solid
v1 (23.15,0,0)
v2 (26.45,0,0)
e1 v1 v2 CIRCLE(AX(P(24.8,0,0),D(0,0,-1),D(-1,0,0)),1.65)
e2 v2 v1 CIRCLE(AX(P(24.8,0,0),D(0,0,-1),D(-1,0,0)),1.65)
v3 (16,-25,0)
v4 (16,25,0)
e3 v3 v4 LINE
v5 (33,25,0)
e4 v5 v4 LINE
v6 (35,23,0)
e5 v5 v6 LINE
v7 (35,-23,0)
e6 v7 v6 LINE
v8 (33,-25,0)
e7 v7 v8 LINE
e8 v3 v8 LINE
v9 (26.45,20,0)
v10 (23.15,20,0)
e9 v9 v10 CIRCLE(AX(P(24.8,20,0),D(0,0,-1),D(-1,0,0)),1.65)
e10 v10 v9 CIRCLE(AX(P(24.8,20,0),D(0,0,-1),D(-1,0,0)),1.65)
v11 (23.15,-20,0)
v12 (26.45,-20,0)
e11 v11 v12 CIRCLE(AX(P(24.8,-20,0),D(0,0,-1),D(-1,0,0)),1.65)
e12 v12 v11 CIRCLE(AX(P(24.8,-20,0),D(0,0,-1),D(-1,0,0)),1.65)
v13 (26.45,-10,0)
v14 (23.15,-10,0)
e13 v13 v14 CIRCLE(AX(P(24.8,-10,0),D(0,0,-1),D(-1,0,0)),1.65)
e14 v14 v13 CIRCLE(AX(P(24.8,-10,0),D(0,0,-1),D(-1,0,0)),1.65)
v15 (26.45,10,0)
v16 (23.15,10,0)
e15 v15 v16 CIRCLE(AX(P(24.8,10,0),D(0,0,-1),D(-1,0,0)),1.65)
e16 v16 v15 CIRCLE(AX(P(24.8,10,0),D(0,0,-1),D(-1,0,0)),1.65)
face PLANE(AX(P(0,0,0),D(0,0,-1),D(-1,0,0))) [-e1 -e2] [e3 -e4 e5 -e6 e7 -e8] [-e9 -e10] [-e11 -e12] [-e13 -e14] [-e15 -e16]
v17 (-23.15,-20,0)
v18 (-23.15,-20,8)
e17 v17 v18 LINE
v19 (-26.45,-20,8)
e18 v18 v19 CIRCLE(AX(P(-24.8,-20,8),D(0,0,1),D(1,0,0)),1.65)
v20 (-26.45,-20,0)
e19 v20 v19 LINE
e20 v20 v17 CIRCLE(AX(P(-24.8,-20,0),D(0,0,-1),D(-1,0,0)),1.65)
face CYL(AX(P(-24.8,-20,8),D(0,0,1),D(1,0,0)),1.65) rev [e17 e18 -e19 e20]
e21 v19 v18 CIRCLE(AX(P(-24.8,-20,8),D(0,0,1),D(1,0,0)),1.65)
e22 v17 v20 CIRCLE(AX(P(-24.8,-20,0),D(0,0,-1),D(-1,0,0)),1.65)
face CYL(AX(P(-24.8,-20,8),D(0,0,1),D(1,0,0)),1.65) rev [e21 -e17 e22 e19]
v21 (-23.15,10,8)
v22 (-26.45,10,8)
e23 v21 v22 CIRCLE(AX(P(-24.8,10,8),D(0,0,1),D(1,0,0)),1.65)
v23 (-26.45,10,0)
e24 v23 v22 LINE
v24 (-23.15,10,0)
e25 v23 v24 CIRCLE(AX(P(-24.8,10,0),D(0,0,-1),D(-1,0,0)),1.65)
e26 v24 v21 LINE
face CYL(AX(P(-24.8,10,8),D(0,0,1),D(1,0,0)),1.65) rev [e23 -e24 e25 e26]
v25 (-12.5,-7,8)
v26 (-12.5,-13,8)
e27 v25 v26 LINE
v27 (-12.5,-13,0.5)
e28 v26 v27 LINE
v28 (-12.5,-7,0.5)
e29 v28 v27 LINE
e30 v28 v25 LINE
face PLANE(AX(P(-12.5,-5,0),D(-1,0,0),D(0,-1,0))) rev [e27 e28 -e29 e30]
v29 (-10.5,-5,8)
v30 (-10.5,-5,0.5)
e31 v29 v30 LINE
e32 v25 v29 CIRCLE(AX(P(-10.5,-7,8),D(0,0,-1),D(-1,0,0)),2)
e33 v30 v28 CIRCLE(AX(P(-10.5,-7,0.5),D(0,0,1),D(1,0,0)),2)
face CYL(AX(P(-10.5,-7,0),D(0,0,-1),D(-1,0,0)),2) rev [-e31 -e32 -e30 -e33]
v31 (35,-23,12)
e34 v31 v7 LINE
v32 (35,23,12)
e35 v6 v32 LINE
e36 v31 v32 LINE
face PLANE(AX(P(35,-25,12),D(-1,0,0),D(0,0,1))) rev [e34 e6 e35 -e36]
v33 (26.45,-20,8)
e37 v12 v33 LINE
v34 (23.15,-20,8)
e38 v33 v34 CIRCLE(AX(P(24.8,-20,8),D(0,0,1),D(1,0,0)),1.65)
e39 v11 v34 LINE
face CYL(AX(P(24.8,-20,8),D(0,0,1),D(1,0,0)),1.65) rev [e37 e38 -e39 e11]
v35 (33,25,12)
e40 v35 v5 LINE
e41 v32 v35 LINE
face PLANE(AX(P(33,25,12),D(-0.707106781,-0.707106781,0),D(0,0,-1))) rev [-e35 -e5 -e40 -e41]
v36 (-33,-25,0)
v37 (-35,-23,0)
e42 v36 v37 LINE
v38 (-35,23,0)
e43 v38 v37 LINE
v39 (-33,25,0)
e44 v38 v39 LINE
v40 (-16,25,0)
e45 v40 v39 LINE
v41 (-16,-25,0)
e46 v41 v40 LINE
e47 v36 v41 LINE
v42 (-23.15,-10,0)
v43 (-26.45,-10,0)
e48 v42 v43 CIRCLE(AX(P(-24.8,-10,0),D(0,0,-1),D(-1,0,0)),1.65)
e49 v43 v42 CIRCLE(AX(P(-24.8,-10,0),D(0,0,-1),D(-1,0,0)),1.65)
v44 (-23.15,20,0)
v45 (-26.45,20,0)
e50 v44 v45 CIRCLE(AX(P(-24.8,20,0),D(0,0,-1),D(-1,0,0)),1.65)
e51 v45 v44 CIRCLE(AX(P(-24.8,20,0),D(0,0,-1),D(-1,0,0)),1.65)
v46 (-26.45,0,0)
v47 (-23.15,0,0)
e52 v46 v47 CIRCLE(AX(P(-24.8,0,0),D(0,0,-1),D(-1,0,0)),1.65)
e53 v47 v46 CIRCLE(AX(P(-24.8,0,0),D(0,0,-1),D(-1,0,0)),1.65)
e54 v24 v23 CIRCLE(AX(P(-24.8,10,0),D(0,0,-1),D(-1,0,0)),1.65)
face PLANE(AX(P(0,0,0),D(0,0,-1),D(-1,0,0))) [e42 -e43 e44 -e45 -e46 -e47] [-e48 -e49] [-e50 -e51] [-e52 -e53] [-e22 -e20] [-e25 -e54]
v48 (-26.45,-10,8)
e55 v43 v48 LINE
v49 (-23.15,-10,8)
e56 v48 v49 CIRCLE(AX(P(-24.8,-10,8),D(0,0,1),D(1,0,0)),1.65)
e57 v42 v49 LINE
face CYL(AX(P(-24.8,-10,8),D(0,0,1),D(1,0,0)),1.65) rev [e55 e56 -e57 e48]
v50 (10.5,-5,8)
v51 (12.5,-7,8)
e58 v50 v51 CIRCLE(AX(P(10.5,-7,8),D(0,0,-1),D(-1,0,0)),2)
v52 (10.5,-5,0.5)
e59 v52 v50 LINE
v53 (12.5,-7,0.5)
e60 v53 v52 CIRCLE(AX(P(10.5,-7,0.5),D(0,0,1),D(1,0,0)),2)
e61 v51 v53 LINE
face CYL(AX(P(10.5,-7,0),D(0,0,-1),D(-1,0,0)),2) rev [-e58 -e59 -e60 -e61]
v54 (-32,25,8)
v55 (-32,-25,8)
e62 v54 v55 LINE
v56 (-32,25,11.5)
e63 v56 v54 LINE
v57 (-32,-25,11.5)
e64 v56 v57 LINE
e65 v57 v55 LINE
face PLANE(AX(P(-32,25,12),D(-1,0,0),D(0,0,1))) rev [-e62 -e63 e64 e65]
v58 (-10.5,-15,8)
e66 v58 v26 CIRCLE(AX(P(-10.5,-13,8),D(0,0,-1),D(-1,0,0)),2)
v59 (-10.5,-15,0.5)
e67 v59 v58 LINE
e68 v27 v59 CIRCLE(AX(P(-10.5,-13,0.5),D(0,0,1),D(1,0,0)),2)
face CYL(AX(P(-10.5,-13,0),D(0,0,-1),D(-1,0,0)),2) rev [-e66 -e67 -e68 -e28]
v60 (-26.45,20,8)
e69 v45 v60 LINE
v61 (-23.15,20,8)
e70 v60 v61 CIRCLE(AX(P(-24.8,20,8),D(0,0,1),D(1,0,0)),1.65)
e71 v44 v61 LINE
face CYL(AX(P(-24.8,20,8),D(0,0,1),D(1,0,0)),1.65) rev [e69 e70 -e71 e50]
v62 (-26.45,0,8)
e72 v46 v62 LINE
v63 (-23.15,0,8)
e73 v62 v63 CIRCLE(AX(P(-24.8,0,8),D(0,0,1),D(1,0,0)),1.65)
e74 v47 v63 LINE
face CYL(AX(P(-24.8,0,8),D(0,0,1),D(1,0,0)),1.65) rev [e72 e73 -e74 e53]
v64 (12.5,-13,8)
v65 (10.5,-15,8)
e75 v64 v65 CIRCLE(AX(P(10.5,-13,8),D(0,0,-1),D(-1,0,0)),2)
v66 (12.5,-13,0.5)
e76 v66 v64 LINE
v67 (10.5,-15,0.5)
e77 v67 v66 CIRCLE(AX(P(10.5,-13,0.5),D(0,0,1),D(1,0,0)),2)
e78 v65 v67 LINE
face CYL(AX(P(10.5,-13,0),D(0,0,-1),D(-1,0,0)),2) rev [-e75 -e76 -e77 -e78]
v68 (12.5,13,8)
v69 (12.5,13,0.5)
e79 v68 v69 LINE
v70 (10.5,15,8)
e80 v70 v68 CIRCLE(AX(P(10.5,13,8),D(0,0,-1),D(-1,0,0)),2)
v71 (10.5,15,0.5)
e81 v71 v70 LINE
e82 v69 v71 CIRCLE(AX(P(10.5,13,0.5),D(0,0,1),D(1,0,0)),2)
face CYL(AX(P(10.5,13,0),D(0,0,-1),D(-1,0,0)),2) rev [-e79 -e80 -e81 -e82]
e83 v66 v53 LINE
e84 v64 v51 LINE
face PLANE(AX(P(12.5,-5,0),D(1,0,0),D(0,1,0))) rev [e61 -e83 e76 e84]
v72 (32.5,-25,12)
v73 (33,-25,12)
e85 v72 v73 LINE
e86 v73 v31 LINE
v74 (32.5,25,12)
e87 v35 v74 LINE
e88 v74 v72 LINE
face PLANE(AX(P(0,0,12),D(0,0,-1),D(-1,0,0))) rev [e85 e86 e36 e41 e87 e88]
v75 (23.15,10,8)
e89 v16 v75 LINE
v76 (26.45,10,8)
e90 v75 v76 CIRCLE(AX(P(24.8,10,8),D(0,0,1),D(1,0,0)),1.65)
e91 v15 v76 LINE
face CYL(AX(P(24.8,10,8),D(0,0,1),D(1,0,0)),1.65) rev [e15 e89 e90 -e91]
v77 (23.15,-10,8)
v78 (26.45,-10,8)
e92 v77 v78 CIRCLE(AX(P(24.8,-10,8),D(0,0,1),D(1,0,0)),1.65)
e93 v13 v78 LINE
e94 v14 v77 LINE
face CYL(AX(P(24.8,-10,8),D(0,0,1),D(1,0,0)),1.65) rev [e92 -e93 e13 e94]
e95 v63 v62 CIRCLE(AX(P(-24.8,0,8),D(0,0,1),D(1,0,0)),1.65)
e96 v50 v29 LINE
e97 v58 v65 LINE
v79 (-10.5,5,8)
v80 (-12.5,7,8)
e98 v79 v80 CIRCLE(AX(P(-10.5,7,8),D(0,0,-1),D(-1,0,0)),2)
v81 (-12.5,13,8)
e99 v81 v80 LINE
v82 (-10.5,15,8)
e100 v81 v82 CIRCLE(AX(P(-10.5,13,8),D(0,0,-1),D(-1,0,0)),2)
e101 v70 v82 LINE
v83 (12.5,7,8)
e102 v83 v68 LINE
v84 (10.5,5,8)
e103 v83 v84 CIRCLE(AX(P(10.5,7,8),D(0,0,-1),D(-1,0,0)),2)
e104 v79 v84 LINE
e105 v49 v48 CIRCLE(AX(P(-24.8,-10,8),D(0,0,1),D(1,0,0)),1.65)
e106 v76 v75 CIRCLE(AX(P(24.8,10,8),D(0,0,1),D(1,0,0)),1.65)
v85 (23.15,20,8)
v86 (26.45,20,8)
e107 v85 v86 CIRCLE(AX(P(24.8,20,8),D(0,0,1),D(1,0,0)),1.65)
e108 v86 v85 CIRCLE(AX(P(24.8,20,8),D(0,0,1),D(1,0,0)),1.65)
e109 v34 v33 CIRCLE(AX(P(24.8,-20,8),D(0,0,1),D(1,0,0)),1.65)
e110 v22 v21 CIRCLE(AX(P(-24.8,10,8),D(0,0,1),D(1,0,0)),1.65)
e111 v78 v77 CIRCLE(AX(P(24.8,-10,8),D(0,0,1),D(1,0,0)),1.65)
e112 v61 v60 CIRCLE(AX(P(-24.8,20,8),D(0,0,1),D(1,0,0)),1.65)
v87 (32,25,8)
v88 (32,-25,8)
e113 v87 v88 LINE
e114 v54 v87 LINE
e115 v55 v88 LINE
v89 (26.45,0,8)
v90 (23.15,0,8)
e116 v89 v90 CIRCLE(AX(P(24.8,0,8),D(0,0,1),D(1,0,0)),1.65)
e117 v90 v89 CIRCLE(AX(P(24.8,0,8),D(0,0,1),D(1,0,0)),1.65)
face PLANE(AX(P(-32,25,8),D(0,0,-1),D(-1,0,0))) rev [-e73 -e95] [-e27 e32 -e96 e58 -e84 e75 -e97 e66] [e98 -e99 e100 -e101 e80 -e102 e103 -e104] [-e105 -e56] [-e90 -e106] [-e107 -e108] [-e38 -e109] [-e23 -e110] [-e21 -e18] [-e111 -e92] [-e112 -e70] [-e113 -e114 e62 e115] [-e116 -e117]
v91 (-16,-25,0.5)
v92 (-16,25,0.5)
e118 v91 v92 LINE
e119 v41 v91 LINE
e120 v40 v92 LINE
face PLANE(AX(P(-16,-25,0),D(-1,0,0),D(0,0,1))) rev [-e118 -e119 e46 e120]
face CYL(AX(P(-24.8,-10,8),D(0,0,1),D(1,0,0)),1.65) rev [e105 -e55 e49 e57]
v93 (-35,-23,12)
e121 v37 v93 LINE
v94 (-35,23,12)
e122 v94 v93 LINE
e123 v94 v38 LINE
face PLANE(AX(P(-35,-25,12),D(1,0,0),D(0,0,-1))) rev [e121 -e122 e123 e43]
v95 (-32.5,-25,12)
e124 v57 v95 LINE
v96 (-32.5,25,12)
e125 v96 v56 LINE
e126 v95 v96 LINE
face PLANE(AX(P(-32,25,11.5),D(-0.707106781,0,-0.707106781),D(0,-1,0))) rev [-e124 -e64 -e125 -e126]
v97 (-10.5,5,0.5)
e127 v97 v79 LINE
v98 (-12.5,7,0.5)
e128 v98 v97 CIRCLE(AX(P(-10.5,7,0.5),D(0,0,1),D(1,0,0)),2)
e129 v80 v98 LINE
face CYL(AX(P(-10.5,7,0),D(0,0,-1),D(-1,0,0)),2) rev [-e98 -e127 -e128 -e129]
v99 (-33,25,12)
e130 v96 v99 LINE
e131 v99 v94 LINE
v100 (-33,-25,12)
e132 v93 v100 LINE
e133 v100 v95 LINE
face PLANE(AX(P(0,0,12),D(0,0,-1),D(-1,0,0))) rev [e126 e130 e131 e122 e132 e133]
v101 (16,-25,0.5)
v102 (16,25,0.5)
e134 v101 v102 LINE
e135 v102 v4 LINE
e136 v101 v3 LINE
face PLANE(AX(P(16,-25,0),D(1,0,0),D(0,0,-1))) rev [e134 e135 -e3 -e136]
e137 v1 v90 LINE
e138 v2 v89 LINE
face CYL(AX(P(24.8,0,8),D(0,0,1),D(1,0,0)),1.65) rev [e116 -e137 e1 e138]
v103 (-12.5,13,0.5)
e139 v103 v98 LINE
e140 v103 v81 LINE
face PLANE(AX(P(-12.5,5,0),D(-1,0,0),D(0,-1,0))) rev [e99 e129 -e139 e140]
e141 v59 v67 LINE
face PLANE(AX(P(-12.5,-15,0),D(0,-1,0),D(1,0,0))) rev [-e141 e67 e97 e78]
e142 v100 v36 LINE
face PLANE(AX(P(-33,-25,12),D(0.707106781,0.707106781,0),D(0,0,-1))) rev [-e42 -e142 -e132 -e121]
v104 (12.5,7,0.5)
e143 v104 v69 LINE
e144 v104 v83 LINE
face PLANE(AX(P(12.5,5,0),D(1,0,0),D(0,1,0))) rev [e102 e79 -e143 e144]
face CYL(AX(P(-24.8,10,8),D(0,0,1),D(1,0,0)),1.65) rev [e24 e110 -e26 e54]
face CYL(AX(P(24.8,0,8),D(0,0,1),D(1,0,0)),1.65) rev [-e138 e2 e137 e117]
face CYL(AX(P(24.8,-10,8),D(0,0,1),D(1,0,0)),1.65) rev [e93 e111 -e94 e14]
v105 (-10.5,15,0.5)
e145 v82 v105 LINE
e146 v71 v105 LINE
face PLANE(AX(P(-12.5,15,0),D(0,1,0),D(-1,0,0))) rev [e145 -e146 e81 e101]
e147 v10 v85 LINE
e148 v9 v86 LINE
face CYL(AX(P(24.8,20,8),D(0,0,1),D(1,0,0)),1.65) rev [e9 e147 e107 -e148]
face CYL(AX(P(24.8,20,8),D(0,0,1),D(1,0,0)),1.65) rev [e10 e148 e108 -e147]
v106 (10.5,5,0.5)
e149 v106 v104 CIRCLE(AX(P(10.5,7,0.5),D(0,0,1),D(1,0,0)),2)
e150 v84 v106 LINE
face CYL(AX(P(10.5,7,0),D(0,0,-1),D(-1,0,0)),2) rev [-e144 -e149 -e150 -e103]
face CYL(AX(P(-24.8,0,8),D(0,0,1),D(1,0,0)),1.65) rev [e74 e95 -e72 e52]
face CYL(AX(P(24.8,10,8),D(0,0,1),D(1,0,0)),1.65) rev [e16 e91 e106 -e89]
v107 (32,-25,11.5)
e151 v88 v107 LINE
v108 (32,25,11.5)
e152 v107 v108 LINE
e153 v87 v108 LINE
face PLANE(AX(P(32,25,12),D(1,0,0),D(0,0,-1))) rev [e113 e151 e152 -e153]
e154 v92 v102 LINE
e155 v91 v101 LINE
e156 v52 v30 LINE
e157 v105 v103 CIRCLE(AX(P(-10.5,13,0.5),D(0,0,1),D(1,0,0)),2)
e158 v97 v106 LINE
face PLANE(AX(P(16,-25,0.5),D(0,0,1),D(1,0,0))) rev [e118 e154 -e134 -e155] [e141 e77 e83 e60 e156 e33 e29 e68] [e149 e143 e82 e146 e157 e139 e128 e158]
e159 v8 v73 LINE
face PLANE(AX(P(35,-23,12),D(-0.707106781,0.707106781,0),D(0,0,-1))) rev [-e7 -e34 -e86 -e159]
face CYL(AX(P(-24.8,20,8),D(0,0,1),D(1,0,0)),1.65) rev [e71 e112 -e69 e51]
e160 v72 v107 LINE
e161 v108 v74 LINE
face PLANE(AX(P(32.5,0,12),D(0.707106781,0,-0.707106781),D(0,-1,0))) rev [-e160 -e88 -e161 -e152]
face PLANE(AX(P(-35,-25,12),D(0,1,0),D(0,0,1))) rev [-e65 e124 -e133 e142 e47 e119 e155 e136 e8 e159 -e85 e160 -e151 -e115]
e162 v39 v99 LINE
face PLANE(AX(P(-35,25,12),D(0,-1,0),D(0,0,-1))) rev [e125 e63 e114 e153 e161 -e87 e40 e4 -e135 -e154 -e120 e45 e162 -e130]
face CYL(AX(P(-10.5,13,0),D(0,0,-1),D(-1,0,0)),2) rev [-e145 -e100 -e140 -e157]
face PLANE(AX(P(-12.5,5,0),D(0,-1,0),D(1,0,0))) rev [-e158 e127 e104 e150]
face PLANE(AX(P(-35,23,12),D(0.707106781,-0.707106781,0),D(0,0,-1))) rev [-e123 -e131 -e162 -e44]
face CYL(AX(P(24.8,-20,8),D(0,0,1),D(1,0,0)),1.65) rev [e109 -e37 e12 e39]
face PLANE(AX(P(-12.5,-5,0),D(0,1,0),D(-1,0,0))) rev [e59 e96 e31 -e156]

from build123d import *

# Parameters (mm, degrees)
SKETCH1_W           = 70
SKETCH1_H           = 50
BOSS_EXTRUDE1_DEPTH = 12
SKETCH2_W           = 64
SKETCH2_H           = 4
CUT_EXTRUDE1_DEPTH  = 63.20128616
CHAMFER1_SIZE       = 0.5
SKETCH3_W           = 32
SKETCH3_H           = 0.5
CUT_EXTRUDE2_DEPTH  = 63.20128616
LPATTERN1_COUNT     = 5
LPATTERN1_PITCH     = 10
SKETCH7_W           = 25
SKETCH7_H           = 10
CUT_EXTRUDE3_DEPTH  = 44.749285708
FILLET1_R           = 2
CHAMFER2_SIZE       = 2


with BuildPart() as part:
    # Sketch1 → Boss-Extrude1 (new body)
    with BuildSketch(Plane.XY):
        Rectangle(SKETCH1_W, SKETCH1_H)
    extrude(amount=BOSS_EXTRUDE1_DEPTH)

    # Sketch2 → Cut-Extrude1 (cut, through all)
    with BuildSketch(Plane.XZ.offset(25)):
        with Locations((0, 10)):
            Rectangle(SKETCH2_W, SKETCH2_H)
    extrude(amount=-CUT_EXTRUDE1_DEPTH, mode=Mode.SUBTRACT)

    # Chamfer1
    chamfer1_edges = [part.edges().sort_by_distance(p)[0] for p in [
        (-32, 0, 12),
        (32, 0, 12),
    ]]
    chamfer(chamfer1_edges, length=CHAMFER1_SIZE)

    # Sketch3 → Cut-Extrude2 (cut, through all)
    with BuildSketch(Plane(origin=(0, 25, 0), x_dir=(1, 0, 0), z_dir=(0, 1, 0))):
        with Locations((0, -0.25)):
            Rectangle(SKETCH3_W, SKETCH3_H)
    extrude(amount=-CUT_EXTRUDE2_DEPTH, mode=Mode.SUBTRACT)

    # Sketch6 → M4 Tapped Hole1 (revolve, cut)
    with BuildSketch(Plane(origin=(-24.8, 20, 8), x_dir=(0, -1, 0), z_dir=(1, 0, 0))):
        Polygon((0, 0), (0, 12.491420021), (1.65, 11.5), (1.65, 0), align=None)
    m4_tapped_hole1 = revolve(axis=Axis((-24.8, 20, 14.35), (0, 0, -1)), mode=Mode.SUBTRACT)

    # LPattern1: M4 Tapped Hole1 ×5
    with Locations(*[(0, -i * LPATTERN1_PITCH, 0) for i in range(1, LPATTERN1_COUNT)]):
        add(m4_tapped_hole1, mode=Mode.SUBTRACT)

    # Mirror1: M4 Tapped Hole1 across plane
    add(m4_tapped_hole1.mirror(Plane(origin=(0, 0, 0), x_dir=(0, 0, 1), z_dir=(1, 0, 0))), mode=Mode.SUBTRACT)

    # Mirror1 copy 1 sketch → Mirror1 copy 1 (revolve, cut)
    with BuildSketch(Plane(origin=(24.8, 10, 8), x_dir=(0, -1, 0), z_dir=(-1, 0, 0))):
        Polygon((0, 0), (0, -12.491420021), (1.65, -11.5), (1.65, 0), align=None)
    revolve(axis=Axis((24.8, 10, 14.35), (0, 0, 1)), mode=Mode.SUBTRACT)

    # Mirror1 copy 2 sketch → Mirror1 copy 2 (revolve, cut)
    with BuildSketch(Plane(origin=(24.8, 0, 8), x_dir=(0, -1, 0), z_dir=(-1, 0, 0))):
        Polygon((0, 0), (0, -12.491420021), (1.65, -11.5), (1.65, 0), align=None)
    revolve(axis=Axis((24.8, 0, 14.35), (0, 0, 1)), mode=Mode.SUBTRACT)

    # Mirror1 copy 3 sketch → Mirror1 copy 3 (revolve, cut)
    with BuildSketch(Plane(origin=(24.8, -10, 8), x_dir=(0, -1, 0), z_dir=(-1, 0, 0))):
        Polygon((0, 0), (0, -12.491420021), (1.65, -11.5), (1.65, 0), align=None)
    revolve(axis=Axis((24.8, -10, 14.35), (0, 0, 1)), mode=Mode.SUBTRACT)

    # Mirror1 copy 4 sketch → Mirror1 copy 4 (revolve, cut)
    with BuildSketch(Plane(origin=(24.8, -20, 8), x_dir=(0, -1, 0), z_dir=(-1, 0, 0))):
        Polygon((0, 0), (0, -12.491420021), (1.65, -11.5), (1.65, 0), align=None)
    revolve(axis=Axis((24.8, -20, 14.35), (0, 0, 1)), mode=Mode.SUBTRACT)

    # Sketch7 → Cut-Extrude3 (cut, through all)
    with BuildSketch(Plane.XY.offset(8)):
        with Locations((0, -10)):
            Rectangle(SKETCH7_W, SKETCH7_H)
        with Locations((0, 10)):
            Rectangle(SKETCH7_W, SKETCH7_H)
    extrude(amount=-CUT_EXTRUDE3_DEPTH, mode=Mode.SUBTRACT)

    # Fillet1
    fillet1_edges = [part.edges().sort_by_distance(p)[0] for p in [
        (-12.5, -15, 4.25),
        (-12.5, -5, 4.25),
        (12.5, -5, 4.25),
        (12.5, -15, 4.25),
        (12.5, 5, 4.25),
        (-12.5, 5, 4.25),
        (-12.5, 15, 4.25),
        (12.5, 15, 4.25),
    ]]
    fillet(fillet1_edges, radius=FILLET1_R)

    # Chamfer2
    chamfer2_edges = [part.edges().sort_by_distance(p)[0] for p in [
        (35, -25, 6),
        (-35, -25, 6),
        (-35, 25, 6),
        (35, 25, 6),
    ]]
    chamfer(chamfer2_edges, length=CHAMFER2_SIZE)


solid = part.part
